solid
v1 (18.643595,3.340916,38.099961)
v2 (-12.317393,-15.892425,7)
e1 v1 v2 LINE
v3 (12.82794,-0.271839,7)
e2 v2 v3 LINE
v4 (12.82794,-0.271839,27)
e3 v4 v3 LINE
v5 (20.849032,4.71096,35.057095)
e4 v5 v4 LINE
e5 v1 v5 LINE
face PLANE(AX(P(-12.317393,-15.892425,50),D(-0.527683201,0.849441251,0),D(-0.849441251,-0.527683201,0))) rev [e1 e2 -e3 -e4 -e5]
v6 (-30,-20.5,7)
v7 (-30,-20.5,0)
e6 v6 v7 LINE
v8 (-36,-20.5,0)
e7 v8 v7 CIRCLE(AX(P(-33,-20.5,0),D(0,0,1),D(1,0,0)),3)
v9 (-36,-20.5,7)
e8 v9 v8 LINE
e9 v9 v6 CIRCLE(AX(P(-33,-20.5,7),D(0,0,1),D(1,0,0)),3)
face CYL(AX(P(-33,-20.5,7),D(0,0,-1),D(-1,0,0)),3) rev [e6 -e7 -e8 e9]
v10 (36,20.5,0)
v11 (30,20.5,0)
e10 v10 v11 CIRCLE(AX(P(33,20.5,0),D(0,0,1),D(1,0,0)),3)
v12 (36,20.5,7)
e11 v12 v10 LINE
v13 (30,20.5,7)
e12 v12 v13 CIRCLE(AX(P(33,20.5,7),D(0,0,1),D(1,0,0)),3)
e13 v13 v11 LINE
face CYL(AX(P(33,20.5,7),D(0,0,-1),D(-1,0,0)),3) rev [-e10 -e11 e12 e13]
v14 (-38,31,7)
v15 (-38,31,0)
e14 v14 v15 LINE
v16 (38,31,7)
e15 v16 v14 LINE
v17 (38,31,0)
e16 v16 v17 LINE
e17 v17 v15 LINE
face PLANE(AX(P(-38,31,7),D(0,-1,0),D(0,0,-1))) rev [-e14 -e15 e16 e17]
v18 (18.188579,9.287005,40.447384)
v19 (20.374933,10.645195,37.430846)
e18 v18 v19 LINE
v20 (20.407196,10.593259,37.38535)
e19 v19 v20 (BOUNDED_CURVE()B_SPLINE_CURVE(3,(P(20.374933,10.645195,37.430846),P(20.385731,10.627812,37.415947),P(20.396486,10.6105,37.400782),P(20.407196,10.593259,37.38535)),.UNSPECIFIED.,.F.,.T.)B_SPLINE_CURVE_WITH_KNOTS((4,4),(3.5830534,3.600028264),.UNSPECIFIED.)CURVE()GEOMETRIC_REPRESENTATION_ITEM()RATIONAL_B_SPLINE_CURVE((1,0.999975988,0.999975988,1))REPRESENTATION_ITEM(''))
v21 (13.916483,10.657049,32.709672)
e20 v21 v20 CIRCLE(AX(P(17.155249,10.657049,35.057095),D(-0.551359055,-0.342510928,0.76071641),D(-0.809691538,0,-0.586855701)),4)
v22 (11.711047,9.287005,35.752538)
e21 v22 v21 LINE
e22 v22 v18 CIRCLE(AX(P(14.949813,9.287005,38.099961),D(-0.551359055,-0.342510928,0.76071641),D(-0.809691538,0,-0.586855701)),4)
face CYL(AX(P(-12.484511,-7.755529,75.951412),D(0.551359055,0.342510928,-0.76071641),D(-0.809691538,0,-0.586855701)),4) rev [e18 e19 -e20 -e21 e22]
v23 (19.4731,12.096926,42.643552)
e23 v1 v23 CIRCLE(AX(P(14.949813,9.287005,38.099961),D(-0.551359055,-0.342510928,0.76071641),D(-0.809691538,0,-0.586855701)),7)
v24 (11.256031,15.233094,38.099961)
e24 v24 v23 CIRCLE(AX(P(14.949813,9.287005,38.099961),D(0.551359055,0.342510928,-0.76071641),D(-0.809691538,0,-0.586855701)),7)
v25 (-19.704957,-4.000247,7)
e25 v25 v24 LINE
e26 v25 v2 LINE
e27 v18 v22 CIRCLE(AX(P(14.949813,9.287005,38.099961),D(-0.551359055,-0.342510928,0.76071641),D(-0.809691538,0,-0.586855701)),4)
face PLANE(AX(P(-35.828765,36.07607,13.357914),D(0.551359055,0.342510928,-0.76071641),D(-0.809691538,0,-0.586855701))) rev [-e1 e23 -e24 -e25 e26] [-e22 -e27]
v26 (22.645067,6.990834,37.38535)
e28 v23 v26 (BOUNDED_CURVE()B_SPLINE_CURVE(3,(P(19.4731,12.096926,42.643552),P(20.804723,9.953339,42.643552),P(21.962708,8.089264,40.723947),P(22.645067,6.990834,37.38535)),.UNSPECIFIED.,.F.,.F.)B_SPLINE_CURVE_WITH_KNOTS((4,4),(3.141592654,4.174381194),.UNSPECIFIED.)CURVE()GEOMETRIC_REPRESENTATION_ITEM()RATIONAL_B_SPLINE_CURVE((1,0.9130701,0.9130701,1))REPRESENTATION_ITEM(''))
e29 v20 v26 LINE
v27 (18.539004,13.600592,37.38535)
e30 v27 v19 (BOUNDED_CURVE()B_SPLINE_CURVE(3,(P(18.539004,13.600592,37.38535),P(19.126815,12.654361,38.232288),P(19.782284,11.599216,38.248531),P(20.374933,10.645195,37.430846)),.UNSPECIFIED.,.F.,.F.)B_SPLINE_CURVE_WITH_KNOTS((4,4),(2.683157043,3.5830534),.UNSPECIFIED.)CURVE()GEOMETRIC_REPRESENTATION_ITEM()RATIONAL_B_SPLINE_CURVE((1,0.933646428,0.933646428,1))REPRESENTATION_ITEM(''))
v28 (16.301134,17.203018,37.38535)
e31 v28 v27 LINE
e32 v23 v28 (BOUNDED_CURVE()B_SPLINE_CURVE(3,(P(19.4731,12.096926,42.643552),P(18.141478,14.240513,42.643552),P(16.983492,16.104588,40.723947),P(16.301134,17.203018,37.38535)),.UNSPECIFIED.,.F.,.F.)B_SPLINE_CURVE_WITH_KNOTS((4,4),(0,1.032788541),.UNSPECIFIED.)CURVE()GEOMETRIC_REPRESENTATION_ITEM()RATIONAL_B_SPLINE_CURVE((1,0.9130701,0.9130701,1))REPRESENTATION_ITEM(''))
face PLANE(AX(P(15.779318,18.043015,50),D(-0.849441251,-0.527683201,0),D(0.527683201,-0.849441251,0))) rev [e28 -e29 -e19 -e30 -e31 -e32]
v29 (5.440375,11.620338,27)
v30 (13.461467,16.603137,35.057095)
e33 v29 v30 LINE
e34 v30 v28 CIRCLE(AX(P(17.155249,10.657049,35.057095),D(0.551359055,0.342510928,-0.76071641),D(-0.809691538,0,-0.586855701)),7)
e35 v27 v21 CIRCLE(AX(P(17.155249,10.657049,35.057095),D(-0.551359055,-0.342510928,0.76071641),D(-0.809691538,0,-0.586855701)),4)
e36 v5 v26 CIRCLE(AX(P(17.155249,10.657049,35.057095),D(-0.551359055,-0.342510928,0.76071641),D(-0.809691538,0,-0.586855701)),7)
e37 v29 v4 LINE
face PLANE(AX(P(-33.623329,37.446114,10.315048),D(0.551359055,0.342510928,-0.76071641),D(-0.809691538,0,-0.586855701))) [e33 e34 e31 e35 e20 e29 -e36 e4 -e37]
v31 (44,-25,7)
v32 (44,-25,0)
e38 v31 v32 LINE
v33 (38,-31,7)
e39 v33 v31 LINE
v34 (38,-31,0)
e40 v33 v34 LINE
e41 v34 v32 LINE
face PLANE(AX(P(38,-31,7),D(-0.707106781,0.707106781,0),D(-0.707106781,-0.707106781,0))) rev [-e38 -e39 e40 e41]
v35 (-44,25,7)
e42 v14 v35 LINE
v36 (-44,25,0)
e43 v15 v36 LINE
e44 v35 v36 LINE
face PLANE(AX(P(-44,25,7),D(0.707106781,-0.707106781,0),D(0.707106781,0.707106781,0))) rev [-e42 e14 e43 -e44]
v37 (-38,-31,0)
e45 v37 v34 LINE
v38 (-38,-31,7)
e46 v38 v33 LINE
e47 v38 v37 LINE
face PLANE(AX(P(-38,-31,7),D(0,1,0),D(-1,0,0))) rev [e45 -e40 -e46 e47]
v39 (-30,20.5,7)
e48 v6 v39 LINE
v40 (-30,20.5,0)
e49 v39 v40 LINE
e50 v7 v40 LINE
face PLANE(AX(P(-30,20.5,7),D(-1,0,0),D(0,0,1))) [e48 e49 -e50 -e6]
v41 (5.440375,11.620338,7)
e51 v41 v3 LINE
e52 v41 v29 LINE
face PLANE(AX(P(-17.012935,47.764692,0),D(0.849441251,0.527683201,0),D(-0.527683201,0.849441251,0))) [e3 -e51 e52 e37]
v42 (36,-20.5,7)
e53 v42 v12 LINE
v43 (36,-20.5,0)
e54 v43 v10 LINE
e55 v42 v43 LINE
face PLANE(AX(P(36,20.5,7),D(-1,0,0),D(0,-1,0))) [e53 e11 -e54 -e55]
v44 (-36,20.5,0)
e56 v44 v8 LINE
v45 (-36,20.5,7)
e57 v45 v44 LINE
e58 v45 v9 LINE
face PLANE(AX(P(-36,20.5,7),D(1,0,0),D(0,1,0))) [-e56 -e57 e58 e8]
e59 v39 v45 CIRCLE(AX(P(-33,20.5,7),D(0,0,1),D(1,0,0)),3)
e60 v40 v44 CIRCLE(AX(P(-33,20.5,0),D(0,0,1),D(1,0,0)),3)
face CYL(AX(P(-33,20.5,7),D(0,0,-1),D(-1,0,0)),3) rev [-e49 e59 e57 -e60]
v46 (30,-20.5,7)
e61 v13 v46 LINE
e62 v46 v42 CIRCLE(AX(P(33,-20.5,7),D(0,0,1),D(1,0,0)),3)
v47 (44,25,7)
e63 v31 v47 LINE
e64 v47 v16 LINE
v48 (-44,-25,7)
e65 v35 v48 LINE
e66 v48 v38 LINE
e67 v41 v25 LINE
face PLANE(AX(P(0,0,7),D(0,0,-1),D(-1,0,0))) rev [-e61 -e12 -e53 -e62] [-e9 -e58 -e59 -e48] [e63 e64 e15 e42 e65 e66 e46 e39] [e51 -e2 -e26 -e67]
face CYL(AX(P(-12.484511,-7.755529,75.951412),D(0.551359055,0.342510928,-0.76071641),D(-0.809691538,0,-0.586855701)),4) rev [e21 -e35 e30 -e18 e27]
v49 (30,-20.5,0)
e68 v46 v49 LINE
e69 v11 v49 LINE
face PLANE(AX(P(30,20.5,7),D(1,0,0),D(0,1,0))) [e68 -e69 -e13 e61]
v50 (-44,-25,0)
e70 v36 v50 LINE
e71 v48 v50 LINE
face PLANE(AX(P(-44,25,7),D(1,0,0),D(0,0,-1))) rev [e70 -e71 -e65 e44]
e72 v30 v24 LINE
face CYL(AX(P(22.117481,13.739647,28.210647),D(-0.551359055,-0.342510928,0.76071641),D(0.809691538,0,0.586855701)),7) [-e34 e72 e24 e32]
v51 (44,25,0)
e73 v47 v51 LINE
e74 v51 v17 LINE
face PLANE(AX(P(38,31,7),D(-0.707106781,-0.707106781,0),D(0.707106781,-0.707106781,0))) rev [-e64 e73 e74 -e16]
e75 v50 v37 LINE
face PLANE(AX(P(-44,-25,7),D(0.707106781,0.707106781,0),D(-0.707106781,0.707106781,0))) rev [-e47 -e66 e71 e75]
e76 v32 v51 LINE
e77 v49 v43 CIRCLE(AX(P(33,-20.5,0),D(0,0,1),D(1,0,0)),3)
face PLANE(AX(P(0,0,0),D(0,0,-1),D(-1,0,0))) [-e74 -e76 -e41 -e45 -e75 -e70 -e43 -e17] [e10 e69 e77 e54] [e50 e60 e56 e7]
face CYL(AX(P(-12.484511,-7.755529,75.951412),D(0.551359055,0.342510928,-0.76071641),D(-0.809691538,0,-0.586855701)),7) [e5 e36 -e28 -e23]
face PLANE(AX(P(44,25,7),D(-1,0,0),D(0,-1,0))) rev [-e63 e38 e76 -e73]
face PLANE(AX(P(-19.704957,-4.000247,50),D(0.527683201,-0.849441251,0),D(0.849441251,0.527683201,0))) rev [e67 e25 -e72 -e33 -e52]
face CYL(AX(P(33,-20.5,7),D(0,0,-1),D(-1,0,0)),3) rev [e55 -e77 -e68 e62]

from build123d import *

# Parameters (mm, degrees)
BASE_PLATE_DEPTH            = 7
ANGLED_BLOCK_DEPTH          = 50
BLOCK_NOTCH_CUT_DEPTH       = 74.464277033
BLOCK_NOTCH_CUT_DEPTH_BACK  = 74.464277033
BLOCK_RECESS_CUT_DEPTH      = 72.480306495
BLOCK_RECESS_CUT_DEPTH_BACK = 13
BLOCK_RECESS_SKETCH_R       = 4


with BuildPart() as part:
    # Base Plate Sketch → Base Plate (new body)
    with BuildSketch(Plane.XY):
        Polygon((-44, 25), (-38, 31), (38, 31), (44, 25), (44, -25), (38, -31), (-38, -31), (-44, -25), align=None)
        with BuildLine():
            Line((-30, 20.5), (-30, -20.5))
            ThreePointArc((-30, -20.5), (-33, -23.5), (-36, -20.5))
            Line((-36, -20.5), (-36, 20.5))
            ThreePointArc((-36, 20.5), (-33, 23.5), (-30, 20.5))
        make_face(mode=Mode.SUBTRACT)
        with BuildLine():
            Line((36, 20.5), (36, -20.5))
            ThreePointArc((36, -20.5), (33, -23.5), (30, -20.5))
            Line((30, -20.5), (30, 20.5))
            ThreePointArc((30, 20.5), (33, 23.5), (36, 20.5))
        make_face(mode=Mode.SUBTRACT)
    extrude(amount=BASE_PLATE_DEPTH)

    # Angled Block Sketch → Angled Block (add)
    with BuildSketch(Plane.XY):
        Polygon((-19.704957389, -4.000247215), (-12.317392569, -15.892424729), (23.166882613, 6.150837127), (15.779317794, 18.043014641), align=None)
    extrude(amount=ANGLED_BLOCK_DEPTH)

    # Block Notch Sketch → Block Notch Cut (cut, two sides: drawn at the far end of the back side and taken through both)
    with BuildSketch(Plane(origin=(0, 0, 0), x_dir=(0.8494412510349073, 0.5276832014004726, 0), z_dir=(0.5276832014004726, -0.8494412510349073, 0)).offset(-BLOCK_NOTCH_CUT_DEPTH_BACK)):
        Polygon((-18.849066913, 50), (-18.849066913, 7), (22.924599176, 42.643551505), (22.924599176, 50), align=None)
        Polygon((10.753136621, 27), (10.753136621, 7), (15.483777963, 7), (22.924599176, 7), (22.924599176, 37.385350224), align=None)
    extrude(amount=BLOCK_NOTCH_CUT_DEPTH + BLOCK_NOTCH_CUT_DEPTH_BACK, mode=Mode.SUBTRACT)

    # Block Recess Sketch → Block Recess Cut (cut, two sides: drawn at the far end of the back side and taken through both)
    with BuildSketch(Plane(origin=(-9.681672009, -6.014372005, 13.357913864), x_dir=(0.8342680576474281, -0.22636189915410374, 0.5027495386378142), z_dir=(-0.5513590554159673, -0.3425109283644645, 0.7607164096834806)).offset(-BLOCK_RECESS_CUT_DEPTH_BACK)):
        with Locations(Location((29.524664999, 24.110272289, 0), (0, 0, 193.941739612))):
            Circle(BLOCK_RECESS_SKETCH_R)
        with BuildLine():
            ThreePointArc((36.524664999, 24.110272289), (35.848943941, 21.109689701), (33.952237609, 18.688409068))
            Line((33.952237609, 18.688409068), (39.374100831, 23.115981696))
            Line((39.374100831, 23.115981696), (34.946528251, 28.53784486))
            ThreePointArc((34.946528251, 28.53784486), (36.118337828, 26.460480496), (36.524664999, 24.110272289))
        make_face()
        with BuildLine():
            Line((30.518955591, 33.959708121), (25.097092428, 29.532135541))
            ThreePointArc((25.097092428, 29.532135541), (30.227734682, 31.07487515), (34.946528251, 28.53784486))
            Line((34.946528251, 28.53784486), (30.518955591, 33.959708121))
        make_face()
    extrude(amount=BLOCK_RECESS_CUT_DEPTH + BLOCK_RECESS_CUT_DEPTH_BACK, mode=Mode.SUBTRACT)


solid = part.part
